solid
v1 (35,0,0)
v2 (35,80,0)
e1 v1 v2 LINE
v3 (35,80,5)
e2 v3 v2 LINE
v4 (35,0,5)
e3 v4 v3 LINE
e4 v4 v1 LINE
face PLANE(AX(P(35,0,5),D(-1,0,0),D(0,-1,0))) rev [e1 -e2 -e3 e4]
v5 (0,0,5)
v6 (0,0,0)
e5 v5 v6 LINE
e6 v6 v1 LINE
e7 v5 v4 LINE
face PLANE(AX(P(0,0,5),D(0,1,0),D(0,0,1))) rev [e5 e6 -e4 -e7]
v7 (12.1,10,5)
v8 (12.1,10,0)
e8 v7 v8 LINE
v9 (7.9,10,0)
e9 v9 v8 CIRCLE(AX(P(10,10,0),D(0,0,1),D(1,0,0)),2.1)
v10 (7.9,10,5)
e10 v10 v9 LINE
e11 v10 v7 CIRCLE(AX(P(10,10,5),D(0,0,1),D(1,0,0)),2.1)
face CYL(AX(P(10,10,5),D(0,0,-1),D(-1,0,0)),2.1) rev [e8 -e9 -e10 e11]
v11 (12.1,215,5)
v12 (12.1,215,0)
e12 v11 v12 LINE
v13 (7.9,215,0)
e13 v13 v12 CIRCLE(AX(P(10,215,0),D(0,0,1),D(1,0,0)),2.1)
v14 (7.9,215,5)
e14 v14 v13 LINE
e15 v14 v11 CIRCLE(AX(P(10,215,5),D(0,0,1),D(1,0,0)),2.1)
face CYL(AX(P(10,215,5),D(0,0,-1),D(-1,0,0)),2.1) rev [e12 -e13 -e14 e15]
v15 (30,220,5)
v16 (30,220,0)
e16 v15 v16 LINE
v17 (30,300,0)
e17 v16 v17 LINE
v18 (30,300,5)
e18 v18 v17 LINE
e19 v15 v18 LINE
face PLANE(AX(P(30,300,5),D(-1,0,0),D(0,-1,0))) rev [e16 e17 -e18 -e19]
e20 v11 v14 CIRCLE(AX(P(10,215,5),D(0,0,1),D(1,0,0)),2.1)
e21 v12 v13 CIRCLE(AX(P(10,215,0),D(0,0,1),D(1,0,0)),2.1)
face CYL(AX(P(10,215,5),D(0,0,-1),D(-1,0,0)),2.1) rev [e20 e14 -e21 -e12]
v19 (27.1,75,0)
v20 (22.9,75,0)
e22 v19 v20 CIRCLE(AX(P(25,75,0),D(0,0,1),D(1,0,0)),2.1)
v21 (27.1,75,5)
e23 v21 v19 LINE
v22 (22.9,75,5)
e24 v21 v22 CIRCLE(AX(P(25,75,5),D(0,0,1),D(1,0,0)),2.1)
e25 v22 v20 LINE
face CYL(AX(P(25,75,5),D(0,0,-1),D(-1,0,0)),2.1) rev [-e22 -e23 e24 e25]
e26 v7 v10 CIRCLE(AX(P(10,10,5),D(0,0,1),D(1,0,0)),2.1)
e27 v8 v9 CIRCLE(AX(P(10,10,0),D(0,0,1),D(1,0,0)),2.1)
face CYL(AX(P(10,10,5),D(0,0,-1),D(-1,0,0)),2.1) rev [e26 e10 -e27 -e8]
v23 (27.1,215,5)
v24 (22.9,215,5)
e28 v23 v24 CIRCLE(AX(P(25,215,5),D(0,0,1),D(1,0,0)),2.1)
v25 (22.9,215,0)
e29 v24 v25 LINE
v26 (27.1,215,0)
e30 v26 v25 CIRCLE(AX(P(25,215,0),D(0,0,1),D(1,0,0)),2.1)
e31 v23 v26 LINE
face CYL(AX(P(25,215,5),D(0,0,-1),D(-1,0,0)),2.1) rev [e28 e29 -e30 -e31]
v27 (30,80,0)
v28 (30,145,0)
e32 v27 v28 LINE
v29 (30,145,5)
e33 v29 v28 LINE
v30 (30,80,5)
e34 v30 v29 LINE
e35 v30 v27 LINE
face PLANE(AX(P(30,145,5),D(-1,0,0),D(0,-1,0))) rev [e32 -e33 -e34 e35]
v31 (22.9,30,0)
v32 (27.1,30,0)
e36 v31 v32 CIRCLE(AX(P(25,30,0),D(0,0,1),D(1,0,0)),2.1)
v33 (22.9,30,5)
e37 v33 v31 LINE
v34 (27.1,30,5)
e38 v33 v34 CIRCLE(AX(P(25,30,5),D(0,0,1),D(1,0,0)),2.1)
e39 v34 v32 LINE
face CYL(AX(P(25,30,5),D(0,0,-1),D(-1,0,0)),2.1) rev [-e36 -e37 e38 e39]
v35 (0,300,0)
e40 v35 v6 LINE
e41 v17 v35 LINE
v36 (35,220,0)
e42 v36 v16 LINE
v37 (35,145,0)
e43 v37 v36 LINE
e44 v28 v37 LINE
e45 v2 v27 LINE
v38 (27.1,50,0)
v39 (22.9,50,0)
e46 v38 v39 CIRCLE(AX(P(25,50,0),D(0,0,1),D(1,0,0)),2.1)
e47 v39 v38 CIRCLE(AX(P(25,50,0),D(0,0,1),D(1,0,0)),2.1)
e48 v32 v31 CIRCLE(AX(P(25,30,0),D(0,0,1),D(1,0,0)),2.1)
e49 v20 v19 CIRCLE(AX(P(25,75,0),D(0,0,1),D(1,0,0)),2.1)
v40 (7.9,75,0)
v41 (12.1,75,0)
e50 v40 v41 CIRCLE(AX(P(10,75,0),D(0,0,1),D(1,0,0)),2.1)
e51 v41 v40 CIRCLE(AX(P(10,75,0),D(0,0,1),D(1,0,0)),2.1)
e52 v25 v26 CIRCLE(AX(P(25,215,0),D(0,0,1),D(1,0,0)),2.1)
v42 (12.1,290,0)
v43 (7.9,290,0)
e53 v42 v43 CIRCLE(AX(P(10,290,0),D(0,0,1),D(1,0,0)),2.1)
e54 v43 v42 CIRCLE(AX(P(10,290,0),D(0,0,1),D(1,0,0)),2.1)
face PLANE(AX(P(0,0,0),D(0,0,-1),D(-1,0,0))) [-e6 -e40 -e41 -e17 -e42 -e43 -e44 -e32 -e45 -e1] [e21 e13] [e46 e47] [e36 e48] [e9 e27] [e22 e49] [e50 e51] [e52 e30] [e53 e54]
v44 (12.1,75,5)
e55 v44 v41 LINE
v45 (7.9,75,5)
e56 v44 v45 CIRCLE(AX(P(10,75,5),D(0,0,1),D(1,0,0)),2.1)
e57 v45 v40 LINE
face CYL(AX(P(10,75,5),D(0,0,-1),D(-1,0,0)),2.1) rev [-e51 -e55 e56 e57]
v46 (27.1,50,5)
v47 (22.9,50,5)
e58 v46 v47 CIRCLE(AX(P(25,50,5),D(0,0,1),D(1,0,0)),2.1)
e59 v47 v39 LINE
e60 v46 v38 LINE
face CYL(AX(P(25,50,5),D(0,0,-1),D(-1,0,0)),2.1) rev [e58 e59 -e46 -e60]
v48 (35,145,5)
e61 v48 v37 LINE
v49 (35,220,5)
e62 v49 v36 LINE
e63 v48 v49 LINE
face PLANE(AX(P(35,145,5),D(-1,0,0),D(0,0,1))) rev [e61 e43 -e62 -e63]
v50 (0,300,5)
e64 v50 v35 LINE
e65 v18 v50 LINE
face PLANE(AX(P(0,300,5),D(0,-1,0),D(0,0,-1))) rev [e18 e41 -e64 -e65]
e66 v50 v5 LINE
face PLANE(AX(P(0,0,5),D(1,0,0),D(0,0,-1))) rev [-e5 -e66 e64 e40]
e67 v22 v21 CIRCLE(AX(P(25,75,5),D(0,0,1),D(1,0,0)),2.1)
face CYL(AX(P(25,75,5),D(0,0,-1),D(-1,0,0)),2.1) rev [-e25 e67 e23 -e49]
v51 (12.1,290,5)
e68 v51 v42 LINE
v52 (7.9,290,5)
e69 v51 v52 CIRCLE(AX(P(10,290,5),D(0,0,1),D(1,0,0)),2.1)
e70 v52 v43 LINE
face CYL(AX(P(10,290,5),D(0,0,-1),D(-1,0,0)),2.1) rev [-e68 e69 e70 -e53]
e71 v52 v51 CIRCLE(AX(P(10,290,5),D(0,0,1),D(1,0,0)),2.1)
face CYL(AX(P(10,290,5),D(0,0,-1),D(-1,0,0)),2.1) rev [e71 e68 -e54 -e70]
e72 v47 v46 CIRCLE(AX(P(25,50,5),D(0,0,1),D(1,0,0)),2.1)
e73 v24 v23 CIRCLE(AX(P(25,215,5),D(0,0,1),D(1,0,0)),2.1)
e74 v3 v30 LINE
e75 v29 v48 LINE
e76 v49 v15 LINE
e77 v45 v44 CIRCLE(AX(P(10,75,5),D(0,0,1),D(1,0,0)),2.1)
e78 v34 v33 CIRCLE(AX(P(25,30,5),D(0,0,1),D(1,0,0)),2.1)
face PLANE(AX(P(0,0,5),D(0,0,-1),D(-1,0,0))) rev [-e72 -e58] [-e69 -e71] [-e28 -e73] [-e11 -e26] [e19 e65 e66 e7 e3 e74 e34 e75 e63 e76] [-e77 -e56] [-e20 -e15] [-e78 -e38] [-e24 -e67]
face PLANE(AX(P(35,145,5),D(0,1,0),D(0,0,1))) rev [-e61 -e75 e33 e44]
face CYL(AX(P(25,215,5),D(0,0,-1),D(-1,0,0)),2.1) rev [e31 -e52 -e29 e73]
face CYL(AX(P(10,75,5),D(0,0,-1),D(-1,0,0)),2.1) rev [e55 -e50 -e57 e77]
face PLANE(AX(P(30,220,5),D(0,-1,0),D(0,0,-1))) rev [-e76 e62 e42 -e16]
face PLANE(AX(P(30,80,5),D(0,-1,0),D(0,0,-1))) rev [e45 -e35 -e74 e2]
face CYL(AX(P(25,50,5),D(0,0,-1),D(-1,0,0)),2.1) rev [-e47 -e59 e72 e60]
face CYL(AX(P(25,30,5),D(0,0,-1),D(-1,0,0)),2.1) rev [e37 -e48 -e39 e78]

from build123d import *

# Parameters (mm, degrees)
SKETCH1_R           = 2.1
BOSS_EXTRUDE1_DEPTH = 5


with BuildPart() as part:
    # Sketch1 → Boss-Extrude1 (new body)
    with BuildSketch(Plane.XY):
        Polygon((30, 300), (30, 220), (35, 220), (35, 145), (30, 145), (30, 80), (35, 80), (35, 0), (0, 0), (0, 300), align=None)
        with Locations((25, 215)):
            Circle(SKETCH1_R, mode=Mode.SUBTRACT)
        with Locations((10, 215)):
            Circle(SKETCH1_R, mode=Mode.SUBTRACT)
        with Locations((25, 75)):
            Circle(SKETCH1_R, mode=Mode.SUBTRACT)
        with Locations((10, 75)):
            Circle(SKETCH1_R, mode=Mode.SUBTRACT)
        with Locations((10, 290)):
            Circle(SKETCH1_R, mode=Mode.SUBTRACT)
        with Locations((10, 10)):
            Circle(SKETCH1_R, mode=Mode.SUBTRACT)
        with Locations((25, 30)):
            Circle(SKETCH1_R, mode=Mode.SUBTRACT)
        with Locations((25, 50)):
            Circle(SKETCH1_R, mode=Mode.SUBTRACT)
    extrude(amount=BOSS_EXTRUDE1_DEPTH)


solid = part.part
